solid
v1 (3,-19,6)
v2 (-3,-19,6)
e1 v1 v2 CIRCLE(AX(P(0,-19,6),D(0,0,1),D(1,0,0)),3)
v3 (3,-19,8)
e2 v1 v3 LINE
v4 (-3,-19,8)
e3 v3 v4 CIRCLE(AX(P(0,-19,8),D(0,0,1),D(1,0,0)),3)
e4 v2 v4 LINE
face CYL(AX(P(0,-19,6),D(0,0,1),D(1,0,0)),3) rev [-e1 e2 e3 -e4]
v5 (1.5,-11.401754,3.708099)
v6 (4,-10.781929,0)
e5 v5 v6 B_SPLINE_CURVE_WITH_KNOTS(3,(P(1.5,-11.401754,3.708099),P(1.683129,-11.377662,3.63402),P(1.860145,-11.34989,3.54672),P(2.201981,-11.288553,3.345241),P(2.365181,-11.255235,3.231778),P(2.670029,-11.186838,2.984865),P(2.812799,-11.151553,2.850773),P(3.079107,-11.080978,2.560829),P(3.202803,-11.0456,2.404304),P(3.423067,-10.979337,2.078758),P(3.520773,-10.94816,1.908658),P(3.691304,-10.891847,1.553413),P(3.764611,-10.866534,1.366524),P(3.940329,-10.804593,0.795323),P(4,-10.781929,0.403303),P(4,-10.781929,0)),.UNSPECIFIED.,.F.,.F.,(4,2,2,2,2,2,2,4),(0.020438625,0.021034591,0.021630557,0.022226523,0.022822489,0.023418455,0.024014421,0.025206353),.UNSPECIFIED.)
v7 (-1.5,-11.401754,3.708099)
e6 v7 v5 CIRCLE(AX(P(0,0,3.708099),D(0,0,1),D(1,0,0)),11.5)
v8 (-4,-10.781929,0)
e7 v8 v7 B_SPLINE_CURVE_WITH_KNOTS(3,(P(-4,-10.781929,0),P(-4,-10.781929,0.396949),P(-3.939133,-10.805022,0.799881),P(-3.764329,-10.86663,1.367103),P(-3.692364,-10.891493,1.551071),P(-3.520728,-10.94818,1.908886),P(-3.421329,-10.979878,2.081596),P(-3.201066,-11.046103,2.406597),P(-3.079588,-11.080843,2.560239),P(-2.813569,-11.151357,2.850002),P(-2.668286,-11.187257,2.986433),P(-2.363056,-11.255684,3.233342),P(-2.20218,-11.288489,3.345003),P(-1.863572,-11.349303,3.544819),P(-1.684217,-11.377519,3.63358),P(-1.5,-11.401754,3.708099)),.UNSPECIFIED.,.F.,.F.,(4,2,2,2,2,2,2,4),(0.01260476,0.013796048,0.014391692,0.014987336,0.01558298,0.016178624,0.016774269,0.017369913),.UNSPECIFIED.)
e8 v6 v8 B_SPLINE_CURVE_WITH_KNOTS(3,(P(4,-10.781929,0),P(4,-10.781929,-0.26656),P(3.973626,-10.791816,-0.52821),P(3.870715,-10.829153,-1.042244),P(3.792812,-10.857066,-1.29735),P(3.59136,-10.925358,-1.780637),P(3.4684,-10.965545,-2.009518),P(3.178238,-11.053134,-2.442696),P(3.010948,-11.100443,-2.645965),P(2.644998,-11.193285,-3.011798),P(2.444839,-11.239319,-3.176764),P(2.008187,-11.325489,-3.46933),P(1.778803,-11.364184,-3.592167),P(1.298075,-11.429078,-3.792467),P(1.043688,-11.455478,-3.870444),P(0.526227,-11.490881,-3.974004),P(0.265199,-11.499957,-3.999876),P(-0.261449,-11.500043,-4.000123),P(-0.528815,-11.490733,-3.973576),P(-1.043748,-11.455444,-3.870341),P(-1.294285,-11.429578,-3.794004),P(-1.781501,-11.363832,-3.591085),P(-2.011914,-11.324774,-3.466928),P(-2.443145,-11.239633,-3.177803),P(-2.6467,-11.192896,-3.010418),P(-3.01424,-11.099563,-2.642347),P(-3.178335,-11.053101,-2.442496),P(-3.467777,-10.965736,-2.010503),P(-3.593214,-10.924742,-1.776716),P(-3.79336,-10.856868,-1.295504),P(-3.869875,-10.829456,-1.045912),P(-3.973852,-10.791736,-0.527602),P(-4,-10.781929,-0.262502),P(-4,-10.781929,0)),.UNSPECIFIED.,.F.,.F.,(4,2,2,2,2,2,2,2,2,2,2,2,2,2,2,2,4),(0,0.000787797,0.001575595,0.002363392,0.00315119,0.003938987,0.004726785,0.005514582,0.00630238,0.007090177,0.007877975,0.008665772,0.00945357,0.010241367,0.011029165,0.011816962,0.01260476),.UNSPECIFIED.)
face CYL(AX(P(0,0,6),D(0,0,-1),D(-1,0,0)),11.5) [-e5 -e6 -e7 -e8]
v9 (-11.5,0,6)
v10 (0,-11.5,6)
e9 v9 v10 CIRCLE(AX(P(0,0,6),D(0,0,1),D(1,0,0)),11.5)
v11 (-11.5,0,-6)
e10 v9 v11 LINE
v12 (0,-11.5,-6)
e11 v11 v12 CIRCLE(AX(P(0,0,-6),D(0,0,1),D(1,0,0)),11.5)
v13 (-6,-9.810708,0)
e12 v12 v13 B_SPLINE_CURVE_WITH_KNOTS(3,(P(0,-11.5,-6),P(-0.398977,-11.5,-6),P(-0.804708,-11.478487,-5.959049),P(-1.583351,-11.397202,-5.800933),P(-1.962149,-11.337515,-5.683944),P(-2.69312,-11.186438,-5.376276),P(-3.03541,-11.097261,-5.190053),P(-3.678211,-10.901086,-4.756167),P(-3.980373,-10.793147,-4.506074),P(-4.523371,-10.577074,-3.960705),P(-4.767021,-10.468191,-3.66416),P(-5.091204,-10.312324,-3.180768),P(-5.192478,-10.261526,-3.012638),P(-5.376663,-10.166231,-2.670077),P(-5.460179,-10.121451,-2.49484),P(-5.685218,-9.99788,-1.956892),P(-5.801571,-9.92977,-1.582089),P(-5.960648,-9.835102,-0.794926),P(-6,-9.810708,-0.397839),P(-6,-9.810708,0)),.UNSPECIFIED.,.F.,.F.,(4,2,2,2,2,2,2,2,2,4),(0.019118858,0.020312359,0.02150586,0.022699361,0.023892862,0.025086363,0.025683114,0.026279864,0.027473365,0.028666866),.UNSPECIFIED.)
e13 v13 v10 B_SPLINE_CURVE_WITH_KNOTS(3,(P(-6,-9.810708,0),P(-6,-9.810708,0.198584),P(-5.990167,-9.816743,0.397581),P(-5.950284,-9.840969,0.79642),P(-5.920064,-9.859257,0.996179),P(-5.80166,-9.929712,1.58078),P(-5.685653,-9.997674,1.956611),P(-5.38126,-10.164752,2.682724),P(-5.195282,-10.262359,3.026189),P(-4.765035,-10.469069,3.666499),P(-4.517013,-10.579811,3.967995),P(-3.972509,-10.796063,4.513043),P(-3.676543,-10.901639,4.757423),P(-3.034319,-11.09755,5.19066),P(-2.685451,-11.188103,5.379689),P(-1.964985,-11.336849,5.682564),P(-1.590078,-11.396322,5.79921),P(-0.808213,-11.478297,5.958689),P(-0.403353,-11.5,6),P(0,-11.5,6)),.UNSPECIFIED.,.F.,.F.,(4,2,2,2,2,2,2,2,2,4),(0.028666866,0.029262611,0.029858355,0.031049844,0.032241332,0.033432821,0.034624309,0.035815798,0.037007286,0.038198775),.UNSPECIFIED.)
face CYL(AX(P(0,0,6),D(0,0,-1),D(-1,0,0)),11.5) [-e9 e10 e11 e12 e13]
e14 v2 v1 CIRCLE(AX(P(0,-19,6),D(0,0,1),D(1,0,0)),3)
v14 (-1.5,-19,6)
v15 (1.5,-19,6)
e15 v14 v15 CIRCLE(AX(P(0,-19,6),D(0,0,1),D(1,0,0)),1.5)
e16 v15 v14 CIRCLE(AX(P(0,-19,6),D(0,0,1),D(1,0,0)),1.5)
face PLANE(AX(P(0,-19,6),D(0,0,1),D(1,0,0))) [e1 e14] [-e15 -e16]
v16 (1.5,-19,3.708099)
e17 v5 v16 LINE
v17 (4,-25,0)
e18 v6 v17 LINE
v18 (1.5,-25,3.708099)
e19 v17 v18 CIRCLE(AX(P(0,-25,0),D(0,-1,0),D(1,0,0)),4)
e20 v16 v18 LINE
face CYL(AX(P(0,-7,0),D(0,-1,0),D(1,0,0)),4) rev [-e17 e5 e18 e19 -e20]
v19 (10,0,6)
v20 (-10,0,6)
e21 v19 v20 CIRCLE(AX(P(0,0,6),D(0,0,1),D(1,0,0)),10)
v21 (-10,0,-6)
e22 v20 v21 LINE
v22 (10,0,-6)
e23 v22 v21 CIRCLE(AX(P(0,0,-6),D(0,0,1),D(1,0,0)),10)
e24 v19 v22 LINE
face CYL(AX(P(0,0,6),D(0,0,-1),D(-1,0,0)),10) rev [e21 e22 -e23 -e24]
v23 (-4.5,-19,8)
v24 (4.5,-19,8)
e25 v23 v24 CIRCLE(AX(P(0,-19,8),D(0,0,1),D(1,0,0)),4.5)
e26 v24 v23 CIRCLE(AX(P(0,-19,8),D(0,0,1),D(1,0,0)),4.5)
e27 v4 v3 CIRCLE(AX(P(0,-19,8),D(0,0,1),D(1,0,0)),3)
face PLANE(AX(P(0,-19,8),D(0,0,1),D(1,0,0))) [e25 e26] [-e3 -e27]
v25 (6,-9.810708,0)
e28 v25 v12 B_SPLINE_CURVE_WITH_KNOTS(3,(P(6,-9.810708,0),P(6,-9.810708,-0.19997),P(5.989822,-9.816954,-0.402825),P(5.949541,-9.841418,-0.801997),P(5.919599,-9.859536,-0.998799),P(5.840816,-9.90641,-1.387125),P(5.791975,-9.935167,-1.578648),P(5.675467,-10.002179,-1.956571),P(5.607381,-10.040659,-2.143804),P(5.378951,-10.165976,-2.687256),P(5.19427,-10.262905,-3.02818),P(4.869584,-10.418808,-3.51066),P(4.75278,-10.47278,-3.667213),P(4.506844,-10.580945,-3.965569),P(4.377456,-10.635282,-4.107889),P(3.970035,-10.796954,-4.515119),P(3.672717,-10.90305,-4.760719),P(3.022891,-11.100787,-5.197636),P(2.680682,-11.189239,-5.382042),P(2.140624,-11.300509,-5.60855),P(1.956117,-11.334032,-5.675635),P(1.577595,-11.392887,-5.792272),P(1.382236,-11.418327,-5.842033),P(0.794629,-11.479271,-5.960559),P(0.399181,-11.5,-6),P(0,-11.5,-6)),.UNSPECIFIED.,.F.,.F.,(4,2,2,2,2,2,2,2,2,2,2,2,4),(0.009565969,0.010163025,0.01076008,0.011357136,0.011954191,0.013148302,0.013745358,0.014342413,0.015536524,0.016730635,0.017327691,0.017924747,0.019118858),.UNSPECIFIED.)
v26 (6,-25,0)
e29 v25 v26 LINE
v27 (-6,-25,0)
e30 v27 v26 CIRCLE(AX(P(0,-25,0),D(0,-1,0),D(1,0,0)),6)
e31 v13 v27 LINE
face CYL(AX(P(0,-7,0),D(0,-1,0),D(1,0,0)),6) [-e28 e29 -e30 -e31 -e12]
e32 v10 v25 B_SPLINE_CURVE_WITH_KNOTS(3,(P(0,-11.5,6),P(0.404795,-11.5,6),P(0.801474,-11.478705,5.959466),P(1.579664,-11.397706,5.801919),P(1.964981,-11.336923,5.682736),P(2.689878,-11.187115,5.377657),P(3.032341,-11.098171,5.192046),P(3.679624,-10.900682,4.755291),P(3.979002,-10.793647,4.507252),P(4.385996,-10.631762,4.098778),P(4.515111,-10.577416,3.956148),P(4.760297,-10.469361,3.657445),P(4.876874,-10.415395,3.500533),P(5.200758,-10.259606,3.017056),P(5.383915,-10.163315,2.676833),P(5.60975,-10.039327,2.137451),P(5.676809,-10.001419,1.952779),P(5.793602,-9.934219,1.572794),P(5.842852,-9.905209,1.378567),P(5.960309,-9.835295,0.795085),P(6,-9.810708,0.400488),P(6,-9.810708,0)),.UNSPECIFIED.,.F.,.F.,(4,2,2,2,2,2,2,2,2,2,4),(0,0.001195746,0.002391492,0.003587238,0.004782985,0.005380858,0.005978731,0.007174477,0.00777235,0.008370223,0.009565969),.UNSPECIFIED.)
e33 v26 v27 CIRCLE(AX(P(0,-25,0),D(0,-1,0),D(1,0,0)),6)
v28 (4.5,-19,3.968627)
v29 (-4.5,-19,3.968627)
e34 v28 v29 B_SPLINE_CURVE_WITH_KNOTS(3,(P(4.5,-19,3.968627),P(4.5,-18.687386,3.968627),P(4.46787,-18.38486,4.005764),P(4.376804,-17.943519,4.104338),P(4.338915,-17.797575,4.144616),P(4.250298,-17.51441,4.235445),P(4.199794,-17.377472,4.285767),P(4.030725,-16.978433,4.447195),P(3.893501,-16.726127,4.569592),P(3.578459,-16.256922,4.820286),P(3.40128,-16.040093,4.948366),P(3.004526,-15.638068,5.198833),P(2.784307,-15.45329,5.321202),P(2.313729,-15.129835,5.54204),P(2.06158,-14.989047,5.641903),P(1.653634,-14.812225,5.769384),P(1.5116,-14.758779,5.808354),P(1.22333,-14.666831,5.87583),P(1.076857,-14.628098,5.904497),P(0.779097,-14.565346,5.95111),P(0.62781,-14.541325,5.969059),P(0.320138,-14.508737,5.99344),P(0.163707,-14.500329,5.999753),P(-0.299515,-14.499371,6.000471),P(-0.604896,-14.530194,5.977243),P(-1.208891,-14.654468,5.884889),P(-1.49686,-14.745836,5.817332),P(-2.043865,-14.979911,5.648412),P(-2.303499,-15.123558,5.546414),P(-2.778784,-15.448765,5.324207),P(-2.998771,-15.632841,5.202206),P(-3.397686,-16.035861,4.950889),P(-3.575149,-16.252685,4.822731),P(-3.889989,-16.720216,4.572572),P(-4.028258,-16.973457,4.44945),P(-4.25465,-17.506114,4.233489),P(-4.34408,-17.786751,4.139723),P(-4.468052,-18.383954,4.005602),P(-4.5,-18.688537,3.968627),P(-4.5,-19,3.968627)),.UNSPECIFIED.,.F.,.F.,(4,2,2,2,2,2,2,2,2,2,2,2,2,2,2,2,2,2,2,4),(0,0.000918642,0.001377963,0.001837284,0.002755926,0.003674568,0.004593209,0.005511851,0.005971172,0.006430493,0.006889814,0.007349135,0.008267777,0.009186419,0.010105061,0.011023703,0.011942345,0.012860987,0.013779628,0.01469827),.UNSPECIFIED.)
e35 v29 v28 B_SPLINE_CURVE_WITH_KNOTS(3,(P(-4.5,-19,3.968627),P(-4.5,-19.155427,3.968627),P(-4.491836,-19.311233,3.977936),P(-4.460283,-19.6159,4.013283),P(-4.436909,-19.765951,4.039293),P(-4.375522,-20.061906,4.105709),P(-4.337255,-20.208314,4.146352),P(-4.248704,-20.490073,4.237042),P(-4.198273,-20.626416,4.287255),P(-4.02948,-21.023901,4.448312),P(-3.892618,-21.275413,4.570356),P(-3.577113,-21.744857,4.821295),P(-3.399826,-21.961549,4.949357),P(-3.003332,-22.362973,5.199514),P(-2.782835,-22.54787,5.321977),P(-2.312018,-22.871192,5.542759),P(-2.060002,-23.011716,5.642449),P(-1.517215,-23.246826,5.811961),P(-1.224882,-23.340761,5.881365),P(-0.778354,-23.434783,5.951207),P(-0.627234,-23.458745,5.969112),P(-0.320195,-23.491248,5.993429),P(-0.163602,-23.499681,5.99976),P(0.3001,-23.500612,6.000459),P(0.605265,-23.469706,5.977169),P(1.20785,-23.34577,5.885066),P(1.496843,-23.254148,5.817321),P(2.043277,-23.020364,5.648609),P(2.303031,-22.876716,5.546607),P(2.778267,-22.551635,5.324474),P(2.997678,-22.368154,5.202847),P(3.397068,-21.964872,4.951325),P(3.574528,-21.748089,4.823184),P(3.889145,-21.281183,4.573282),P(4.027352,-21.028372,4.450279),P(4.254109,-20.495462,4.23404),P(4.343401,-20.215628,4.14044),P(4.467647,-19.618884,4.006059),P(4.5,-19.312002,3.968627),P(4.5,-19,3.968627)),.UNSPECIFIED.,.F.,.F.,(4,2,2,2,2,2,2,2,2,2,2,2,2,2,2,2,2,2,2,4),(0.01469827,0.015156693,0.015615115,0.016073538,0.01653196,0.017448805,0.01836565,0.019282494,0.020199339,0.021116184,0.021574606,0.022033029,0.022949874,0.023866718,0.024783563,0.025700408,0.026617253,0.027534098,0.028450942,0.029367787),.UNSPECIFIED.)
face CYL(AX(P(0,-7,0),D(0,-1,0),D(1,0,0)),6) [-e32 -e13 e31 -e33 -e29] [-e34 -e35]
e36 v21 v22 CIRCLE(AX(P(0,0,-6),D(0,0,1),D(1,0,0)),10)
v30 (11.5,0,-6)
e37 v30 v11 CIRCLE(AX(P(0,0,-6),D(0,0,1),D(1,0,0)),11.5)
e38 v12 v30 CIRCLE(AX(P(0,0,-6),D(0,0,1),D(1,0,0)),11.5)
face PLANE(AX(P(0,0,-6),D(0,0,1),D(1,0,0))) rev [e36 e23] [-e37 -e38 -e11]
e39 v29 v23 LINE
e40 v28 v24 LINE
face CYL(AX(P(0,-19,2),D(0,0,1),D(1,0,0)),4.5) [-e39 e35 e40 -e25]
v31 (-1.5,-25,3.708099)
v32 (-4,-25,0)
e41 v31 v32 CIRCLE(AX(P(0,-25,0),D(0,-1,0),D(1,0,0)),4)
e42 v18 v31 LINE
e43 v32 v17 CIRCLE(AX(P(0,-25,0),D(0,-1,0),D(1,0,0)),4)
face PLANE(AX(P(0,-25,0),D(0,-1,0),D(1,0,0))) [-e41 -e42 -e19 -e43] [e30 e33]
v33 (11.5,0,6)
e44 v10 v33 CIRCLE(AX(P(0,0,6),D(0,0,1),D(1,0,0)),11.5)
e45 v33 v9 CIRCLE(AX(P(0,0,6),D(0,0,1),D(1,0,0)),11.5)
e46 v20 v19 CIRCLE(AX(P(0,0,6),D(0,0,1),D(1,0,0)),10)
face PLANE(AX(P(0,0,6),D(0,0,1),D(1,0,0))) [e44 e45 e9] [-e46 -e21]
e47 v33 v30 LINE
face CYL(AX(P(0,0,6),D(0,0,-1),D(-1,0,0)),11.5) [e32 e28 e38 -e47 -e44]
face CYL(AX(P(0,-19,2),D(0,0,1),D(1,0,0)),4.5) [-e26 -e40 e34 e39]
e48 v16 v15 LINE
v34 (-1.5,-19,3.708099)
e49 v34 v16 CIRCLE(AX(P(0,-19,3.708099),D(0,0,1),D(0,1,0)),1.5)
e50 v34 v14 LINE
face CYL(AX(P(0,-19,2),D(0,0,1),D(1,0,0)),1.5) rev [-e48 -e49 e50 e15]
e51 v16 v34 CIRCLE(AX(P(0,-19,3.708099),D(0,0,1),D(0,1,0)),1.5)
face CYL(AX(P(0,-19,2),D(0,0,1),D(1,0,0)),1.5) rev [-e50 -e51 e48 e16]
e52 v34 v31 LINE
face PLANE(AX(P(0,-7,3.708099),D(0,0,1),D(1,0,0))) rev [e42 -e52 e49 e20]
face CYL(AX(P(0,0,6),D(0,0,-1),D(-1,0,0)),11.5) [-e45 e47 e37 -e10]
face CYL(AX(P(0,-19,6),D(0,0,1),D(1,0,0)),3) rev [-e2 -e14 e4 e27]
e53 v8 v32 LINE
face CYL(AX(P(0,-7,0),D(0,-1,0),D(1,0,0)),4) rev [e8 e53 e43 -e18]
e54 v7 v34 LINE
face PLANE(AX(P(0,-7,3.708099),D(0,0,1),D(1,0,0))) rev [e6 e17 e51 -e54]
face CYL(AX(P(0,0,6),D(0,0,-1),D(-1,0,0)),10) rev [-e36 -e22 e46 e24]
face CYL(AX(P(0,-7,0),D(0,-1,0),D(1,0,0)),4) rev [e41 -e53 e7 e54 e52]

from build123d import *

# Parameters (mm, degrees)
RING_PROFILE_23_20_R      = 11.5
RING_PROFILE_23_20_R_2    = 10
RING_23X12_DEPTH          = 6
STEM_PROFILE_R            = 6
STEM_DEPTH                = 18
RING_START                = -18
RING_CUT_PROFILE_R        = 10
RING_CUT_DEPTH            = 18
SIDE_BOSS_PROFILE_9_R     = 4.5
SIDE_BOSS_9_DEPTH         = 6
SIDE_HOLE_PROFILE_3_R     = 1.5
SIDE_HOLE_3_DEPTH         = 6
COUNTERBORE_PROFILE_6_R   = 3
COUNTERBORE_PROFILE_6_R_2 = 1.5
COUNTERBORE_6X2_DEPTH     = 2
STEM_TRIM_CUT_DEPTH       = 12


with BuildPart() as part:
    # Ring Profile Ø23-Ø20 → Ring Ø23x12 (new, symmetric)
    with BuildSketch(Plane.XY):
        Circle(RING_PROFILE_23_20_R)
        Circle(RING_PROFILE_23_20_R_2, mode=Mode.SUBTRACT)
    extrude(amount=RING_23X12_DEPTH, both=True)

    # Stem Profile → Stem (add)
    with BuildSketch(Plane(origin=(0, -25, 0), x_dir=(-1, 0, 0), z_dir=(0, -1, 0))):
        with Locations(Location((0, 0, 0), (0, 0, 180))):
            Circle(STEM_PROFILE_R)
        with BuildLine():
            Line((-1.5, -3.708099244), (1.5, -3.708099244))
            ThreePointArc((1.5, -3.708099244), (0, 4), (-1.5, -3.708099244))
        make_face(mode=Mode.SUBTRACT)
    extrude(amount=-STEM_DEPTH)

    # Ring Cut Profile → Ring Cut (cut)
    with BuildSketch(Plane.XY.offset(6).offset(RING_START)):
        Circle(RING_CUT_PROFILE_R)
    extrude(amount=RING_CUT_DEPTH, mode=Mode.SUBTRACT)

    # Side Boss Profile Ø9 → Side Boss Ø9 (add)
    with BuildSketch(Plane.XY.offset(8)):
        with Locations((0, -19)):
            Circle(SIDE_BOSS_PROFILE_9_R)
    extrude(amount=-SIDE_BOSS_9_DEPTH)

    # Side Hole Profile Ø3 → Side Hole Ø3 (cut)
    with BuildSketch(Plane.XY.offset(8)):
        with Locations((0, -19)):
            Circle(SIDE_HOLE_PROFILE_3_R)
    extrude(amount=-SIDE_HOLE_3_DEPTH, mode=Mode.SUBTRACT)

    # Counterbore Profile Ø6 → Counterbore Ø6x2 (cut)
    with BuildSketch(Plane.XY.offset(8)):
        with Locations((0, -19)):
            Circle(COUNTERBORE_PROFILE_6_R)
        with Locations((0, -19)):
            Circle(COUNTERBORE_PROFILE_6_R_2, mode=Mode.SUBTRACT)
    extrude(amount=-COUNTERBORE_6X2_DEPTH, mode=Mode.SUBTRACT)

    # Stem Trim Profile → Stem Trim Cut (cut)
    with BuildSketch(Plane.XZ.offset(25)):
        with BuildLine():
            Line((-1.5, 3.708099244), (1.5, 3.708099244))
            ThreePointArc((1.5, 3.708099244), (0, -4), (-1.5, 3.708099244))
        make_face()
    extrude(amount=-STEM_TRIM_CUT_DEPTH, mode=Mode.SUBTRACT)


solid = part.part
